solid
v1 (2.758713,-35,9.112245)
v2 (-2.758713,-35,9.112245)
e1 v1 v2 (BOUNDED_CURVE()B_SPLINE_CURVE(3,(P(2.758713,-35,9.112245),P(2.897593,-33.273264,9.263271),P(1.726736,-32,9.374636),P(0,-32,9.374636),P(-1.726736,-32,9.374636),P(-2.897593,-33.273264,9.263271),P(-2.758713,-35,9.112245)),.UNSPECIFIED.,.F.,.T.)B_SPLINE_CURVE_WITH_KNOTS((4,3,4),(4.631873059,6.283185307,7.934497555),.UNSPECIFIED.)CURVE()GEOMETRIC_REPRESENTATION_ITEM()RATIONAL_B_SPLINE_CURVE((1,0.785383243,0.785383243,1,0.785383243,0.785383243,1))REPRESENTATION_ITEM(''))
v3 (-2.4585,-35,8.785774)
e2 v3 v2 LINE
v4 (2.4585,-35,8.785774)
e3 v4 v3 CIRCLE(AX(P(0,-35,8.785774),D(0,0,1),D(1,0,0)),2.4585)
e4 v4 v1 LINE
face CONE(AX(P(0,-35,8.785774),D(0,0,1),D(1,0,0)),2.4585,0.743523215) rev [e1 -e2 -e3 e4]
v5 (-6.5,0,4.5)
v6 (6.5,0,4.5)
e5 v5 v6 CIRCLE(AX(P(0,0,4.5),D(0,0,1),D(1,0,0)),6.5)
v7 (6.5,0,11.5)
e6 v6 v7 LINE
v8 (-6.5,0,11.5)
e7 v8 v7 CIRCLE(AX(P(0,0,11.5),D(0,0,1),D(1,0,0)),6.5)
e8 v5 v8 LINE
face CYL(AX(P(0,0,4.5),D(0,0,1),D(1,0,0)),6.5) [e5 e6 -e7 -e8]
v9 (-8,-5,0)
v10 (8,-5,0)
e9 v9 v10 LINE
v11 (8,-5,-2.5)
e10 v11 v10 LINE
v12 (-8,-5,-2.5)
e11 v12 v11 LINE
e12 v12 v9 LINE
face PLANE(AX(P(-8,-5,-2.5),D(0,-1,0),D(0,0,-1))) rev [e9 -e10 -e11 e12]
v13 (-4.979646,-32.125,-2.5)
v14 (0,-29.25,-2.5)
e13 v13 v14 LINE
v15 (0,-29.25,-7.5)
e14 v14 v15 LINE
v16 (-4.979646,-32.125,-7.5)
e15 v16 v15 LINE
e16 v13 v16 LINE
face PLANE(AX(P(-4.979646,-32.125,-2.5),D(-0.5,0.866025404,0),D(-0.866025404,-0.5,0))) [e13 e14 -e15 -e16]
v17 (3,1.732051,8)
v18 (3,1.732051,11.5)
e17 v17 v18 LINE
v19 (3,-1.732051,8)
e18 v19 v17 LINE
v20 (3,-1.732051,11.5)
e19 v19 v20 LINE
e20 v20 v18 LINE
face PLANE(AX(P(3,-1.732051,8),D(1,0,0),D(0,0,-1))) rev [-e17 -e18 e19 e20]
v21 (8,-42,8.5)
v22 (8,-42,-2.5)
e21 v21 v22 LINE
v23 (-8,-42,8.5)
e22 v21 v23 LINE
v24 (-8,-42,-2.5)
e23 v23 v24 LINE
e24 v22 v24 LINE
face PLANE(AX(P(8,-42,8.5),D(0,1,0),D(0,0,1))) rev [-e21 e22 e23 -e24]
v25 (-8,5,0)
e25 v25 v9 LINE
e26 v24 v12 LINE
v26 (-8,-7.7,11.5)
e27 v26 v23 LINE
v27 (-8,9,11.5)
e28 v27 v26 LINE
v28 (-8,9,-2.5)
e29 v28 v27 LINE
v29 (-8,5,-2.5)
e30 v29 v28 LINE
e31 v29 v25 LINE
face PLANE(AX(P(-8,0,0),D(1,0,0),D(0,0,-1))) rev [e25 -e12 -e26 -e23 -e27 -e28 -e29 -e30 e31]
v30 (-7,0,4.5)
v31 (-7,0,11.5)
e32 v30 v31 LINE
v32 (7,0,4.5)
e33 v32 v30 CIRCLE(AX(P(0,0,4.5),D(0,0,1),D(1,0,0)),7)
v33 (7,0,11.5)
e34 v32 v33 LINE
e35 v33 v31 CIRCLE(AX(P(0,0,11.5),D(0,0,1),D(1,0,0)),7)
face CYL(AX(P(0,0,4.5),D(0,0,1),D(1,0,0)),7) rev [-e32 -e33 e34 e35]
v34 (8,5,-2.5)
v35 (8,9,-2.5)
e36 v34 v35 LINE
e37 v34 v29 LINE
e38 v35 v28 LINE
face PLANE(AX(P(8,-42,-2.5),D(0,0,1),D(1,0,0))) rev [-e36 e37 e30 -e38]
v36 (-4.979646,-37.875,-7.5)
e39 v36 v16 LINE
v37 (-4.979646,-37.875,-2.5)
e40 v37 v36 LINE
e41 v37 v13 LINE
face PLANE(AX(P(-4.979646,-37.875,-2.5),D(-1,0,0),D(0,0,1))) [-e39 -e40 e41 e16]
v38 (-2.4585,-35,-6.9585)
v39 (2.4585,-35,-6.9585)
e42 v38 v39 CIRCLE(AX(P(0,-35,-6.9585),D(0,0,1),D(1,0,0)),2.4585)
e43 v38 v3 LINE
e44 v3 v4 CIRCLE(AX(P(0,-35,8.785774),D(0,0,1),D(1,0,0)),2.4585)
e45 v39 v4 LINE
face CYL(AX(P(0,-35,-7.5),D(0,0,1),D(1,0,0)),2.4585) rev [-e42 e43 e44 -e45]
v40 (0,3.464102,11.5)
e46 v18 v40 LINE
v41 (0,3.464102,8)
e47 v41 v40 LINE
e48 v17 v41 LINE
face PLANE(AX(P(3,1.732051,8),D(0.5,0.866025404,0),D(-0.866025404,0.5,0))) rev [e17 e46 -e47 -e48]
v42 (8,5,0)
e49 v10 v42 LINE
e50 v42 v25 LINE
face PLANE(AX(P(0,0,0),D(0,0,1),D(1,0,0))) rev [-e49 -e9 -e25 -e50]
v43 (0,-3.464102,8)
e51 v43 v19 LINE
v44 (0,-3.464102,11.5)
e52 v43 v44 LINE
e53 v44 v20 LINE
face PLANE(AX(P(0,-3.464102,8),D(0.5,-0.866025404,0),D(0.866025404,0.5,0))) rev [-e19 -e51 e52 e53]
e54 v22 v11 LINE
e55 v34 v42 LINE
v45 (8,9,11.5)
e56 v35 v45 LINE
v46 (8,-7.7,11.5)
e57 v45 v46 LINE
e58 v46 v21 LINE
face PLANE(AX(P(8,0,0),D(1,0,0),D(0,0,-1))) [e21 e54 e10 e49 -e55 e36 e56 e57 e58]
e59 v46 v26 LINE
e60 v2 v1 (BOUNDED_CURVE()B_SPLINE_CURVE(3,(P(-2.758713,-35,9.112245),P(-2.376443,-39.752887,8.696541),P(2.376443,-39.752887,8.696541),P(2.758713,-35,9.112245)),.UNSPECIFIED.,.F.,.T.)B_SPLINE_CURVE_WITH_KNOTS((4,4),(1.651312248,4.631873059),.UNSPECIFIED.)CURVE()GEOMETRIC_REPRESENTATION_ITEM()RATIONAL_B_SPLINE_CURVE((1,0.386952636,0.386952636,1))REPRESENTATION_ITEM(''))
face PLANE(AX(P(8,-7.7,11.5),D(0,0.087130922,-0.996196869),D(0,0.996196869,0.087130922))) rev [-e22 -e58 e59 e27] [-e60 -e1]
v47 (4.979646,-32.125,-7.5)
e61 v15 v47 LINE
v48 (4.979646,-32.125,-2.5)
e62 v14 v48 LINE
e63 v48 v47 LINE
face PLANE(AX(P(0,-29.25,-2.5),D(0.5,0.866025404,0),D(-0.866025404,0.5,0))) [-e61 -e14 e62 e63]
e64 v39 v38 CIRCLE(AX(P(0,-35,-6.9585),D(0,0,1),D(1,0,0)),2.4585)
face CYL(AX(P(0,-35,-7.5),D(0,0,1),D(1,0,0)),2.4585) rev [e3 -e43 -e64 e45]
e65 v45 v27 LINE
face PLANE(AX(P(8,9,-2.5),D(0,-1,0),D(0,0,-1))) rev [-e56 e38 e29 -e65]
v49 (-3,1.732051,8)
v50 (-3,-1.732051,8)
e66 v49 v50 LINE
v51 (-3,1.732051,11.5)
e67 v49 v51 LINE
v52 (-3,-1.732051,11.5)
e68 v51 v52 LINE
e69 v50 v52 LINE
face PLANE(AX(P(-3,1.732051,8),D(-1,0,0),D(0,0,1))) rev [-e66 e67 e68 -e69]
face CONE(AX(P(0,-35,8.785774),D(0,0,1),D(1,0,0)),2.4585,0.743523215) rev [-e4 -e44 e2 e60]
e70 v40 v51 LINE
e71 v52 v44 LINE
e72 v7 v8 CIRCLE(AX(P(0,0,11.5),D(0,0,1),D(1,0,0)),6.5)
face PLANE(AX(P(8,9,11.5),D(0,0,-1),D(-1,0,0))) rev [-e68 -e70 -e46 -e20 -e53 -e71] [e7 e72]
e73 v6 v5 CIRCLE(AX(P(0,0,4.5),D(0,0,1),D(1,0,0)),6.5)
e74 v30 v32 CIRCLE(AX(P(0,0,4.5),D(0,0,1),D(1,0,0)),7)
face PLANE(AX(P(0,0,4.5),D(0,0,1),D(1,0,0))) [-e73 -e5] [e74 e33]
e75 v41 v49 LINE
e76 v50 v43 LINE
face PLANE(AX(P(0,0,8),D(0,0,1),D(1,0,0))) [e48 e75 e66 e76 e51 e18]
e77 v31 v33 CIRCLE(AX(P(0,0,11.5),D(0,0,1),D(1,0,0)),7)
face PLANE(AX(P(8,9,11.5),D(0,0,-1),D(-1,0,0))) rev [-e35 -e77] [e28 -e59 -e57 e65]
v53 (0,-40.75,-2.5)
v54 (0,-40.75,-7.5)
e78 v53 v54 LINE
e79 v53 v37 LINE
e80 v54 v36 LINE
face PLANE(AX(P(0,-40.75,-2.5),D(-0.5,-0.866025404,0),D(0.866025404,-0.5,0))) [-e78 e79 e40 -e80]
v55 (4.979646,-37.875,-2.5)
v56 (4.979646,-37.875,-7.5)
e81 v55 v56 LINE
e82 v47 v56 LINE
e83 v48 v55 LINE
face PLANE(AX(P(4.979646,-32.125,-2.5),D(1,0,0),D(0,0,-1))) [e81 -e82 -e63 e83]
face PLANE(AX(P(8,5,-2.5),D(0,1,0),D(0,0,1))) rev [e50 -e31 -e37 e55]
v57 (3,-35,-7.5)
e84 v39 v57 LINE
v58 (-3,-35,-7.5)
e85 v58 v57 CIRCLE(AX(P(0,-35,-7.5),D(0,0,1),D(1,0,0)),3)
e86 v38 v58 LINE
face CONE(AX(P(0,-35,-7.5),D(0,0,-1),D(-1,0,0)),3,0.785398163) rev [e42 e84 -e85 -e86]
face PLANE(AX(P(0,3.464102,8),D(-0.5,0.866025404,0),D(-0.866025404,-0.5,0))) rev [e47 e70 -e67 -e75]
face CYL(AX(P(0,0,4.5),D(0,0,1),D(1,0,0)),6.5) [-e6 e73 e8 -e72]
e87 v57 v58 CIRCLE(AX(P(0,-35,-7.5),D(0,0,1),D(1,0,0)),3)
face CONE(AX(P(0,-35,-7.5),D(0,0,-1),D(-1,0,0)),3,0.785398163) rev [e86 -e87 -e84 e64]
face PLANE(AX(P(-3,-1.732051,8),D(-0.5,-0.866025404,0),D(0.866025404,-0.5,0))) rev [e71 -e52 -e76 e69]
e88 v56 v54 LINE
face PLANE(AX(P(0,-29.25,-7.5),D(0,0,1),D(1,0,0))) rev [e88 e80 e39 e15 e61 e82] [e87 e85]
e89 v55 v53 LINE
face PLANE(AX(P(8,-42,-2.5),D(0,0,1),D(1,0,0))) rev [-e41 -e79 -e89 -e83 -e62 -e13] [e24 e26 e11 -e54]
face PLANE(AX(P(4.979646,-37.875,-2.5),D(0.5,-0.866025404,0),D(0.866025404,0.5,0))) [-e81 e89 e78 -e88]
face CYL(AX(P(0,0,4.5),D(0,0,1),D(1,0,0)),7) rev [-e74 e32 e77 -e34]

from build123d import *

# Parameters (mm, degrees)
EXTRUDE_1_DEPTH      = 8
EXTRUDE_1_DEPTH_BACK = 8
SKETCH_2_W           = 16
SKETCH_2_H           = 10
CUT_EXTRUDE_1_DEPTH  = 2.5
SKETCH_3_W           = 5
SKETCH_3_H           = 5.75
SKETCH_4_R           = 11.5
CUT_EXTRUDE_2_DEPTH  = 5
SKETCH_6_R           = 7
SKETCH_6_R_2         = 6.5
CUT_EXTRUDE_3_DEPTH  = 7
CUT_EXTRUDE_4_DEPTH  = 3.5


with BuildPart() as part:
    # 草图1 → 凸台-拉伸1 (new, two sides: drawn at the far end of the back side and taken through both)
    with BuildSketch(Plane(origin=(0, 0, 0), x_dir=(0, 0, -1), z_dir=(1, 0, 0)).offset(-EXTRUDE_1_DEPTH_BACK)):
        Polygon((-11.5, 9), (-11.5, -7.7), (-8.5, -42), (2.5, -42), (2.5, 9), align=None)
    extrude(amount=EXTRUDE_1_DEPTH + EXTRUDE_1_DEPTH_BACK)

    # 草图2 → 切除-拉伸1 (cut)
    with BuildSketch(Plane.XY):
        Rectangle(SKETCH_2_W, SKETCH_2_H)
    extrude(amount=-CUT_EXTRUDE_1_DEPTH, mode=Mode.SUBTRACT)

    # 草图3 → 旋转1 (revolve)
    with BuildSketch(Plane(origin=(0, 0, 0), x_dir=(0, 0, -1), z_dir=(1, 0, 0)), mode=Mode.PRIVATE) as revolve_1_sk:
        with Locations((5, -32.125)):
            Rectangle(SKETCH_3_W, SKETCH_3_H)
    revolve(revolve_1_sk.sketch.rotate(Axis((0, -35, -7.5), (0, 0, 1)), 270), axis=Axis((0, -35, -7.5), (0, 0, 1)))

    # 草图4 → 切除-拉伸2 (cut)
    with BuildSketch(Plane(origin=(0, 0, -7.5), x_dir=(-1, 0, 0), z_dir=(0, 0, -1))):
        with Locations((0, -35)):
            Circle(SKETCH_4_R)
        Polygon((0, -40.75), (4.979646072, -37.875), (4.979646072, -32.125), (0, -29.25), (-4.979646072, -32.125), (-4.979646072, -37.875), align=None, mode=Mode.SUBTRACT)
    extrude(amount=-CUT_EXTRUDE_2_DEPTH, mode=Mode.SUBTRACT)

    # 草图5 → 切除-旋转1 (revolve, cut)
    with BuildSketch(Plane(origin=(0, 0, 0), x_dir=(0, 0, -1), z_dir=(1, 0, 0)), mode=Mode.PRIVATE) as cut_revolve_1_sk:
        Polygon((-9.112244898, -35), (-9.374635569, -32), (-8.785774052, -32.5415), (6.9585, -32.5415), (7.5, -32), (7.5, -35), align=None)
    revolve(cut_revolve_1_sk.sketch.rotate(Axis((0, -35, -7.5), (0, 0, 1)), 270), axis=Axis((0, -35, -7.5), (0, 0, 1)), mode=Mode.SUBTRACT)

    # 草图6 → 切除-拉伸3 (cut)
    with BuildSketch(Plane.XY.offset(11.5)):
        Circle(SKETCH_6_R)
        Circle(SKETCH_6_R_2, mode=Mode.SUBTRACT)
    extrude(amount=-CUT_EXTRUDE_3_DEPTH, mode=Mode.SUBTRACT)

    # 草图7 → 切除-拉伸4 (cut)
    with BuildSketch(Plane.XY.offset(11.5)):
        Polygon((-3, 1.732050808), (-3, -1.732050808), (0, -3.464101615), (3, -1.732050808), (3, 1.732050808), (0, 3.464101615), align=None)
    extrude(amount=-CUT_EXTRUDE_4_DEPTH, mode=Mode.SUBTRACT)


solid = part.part
